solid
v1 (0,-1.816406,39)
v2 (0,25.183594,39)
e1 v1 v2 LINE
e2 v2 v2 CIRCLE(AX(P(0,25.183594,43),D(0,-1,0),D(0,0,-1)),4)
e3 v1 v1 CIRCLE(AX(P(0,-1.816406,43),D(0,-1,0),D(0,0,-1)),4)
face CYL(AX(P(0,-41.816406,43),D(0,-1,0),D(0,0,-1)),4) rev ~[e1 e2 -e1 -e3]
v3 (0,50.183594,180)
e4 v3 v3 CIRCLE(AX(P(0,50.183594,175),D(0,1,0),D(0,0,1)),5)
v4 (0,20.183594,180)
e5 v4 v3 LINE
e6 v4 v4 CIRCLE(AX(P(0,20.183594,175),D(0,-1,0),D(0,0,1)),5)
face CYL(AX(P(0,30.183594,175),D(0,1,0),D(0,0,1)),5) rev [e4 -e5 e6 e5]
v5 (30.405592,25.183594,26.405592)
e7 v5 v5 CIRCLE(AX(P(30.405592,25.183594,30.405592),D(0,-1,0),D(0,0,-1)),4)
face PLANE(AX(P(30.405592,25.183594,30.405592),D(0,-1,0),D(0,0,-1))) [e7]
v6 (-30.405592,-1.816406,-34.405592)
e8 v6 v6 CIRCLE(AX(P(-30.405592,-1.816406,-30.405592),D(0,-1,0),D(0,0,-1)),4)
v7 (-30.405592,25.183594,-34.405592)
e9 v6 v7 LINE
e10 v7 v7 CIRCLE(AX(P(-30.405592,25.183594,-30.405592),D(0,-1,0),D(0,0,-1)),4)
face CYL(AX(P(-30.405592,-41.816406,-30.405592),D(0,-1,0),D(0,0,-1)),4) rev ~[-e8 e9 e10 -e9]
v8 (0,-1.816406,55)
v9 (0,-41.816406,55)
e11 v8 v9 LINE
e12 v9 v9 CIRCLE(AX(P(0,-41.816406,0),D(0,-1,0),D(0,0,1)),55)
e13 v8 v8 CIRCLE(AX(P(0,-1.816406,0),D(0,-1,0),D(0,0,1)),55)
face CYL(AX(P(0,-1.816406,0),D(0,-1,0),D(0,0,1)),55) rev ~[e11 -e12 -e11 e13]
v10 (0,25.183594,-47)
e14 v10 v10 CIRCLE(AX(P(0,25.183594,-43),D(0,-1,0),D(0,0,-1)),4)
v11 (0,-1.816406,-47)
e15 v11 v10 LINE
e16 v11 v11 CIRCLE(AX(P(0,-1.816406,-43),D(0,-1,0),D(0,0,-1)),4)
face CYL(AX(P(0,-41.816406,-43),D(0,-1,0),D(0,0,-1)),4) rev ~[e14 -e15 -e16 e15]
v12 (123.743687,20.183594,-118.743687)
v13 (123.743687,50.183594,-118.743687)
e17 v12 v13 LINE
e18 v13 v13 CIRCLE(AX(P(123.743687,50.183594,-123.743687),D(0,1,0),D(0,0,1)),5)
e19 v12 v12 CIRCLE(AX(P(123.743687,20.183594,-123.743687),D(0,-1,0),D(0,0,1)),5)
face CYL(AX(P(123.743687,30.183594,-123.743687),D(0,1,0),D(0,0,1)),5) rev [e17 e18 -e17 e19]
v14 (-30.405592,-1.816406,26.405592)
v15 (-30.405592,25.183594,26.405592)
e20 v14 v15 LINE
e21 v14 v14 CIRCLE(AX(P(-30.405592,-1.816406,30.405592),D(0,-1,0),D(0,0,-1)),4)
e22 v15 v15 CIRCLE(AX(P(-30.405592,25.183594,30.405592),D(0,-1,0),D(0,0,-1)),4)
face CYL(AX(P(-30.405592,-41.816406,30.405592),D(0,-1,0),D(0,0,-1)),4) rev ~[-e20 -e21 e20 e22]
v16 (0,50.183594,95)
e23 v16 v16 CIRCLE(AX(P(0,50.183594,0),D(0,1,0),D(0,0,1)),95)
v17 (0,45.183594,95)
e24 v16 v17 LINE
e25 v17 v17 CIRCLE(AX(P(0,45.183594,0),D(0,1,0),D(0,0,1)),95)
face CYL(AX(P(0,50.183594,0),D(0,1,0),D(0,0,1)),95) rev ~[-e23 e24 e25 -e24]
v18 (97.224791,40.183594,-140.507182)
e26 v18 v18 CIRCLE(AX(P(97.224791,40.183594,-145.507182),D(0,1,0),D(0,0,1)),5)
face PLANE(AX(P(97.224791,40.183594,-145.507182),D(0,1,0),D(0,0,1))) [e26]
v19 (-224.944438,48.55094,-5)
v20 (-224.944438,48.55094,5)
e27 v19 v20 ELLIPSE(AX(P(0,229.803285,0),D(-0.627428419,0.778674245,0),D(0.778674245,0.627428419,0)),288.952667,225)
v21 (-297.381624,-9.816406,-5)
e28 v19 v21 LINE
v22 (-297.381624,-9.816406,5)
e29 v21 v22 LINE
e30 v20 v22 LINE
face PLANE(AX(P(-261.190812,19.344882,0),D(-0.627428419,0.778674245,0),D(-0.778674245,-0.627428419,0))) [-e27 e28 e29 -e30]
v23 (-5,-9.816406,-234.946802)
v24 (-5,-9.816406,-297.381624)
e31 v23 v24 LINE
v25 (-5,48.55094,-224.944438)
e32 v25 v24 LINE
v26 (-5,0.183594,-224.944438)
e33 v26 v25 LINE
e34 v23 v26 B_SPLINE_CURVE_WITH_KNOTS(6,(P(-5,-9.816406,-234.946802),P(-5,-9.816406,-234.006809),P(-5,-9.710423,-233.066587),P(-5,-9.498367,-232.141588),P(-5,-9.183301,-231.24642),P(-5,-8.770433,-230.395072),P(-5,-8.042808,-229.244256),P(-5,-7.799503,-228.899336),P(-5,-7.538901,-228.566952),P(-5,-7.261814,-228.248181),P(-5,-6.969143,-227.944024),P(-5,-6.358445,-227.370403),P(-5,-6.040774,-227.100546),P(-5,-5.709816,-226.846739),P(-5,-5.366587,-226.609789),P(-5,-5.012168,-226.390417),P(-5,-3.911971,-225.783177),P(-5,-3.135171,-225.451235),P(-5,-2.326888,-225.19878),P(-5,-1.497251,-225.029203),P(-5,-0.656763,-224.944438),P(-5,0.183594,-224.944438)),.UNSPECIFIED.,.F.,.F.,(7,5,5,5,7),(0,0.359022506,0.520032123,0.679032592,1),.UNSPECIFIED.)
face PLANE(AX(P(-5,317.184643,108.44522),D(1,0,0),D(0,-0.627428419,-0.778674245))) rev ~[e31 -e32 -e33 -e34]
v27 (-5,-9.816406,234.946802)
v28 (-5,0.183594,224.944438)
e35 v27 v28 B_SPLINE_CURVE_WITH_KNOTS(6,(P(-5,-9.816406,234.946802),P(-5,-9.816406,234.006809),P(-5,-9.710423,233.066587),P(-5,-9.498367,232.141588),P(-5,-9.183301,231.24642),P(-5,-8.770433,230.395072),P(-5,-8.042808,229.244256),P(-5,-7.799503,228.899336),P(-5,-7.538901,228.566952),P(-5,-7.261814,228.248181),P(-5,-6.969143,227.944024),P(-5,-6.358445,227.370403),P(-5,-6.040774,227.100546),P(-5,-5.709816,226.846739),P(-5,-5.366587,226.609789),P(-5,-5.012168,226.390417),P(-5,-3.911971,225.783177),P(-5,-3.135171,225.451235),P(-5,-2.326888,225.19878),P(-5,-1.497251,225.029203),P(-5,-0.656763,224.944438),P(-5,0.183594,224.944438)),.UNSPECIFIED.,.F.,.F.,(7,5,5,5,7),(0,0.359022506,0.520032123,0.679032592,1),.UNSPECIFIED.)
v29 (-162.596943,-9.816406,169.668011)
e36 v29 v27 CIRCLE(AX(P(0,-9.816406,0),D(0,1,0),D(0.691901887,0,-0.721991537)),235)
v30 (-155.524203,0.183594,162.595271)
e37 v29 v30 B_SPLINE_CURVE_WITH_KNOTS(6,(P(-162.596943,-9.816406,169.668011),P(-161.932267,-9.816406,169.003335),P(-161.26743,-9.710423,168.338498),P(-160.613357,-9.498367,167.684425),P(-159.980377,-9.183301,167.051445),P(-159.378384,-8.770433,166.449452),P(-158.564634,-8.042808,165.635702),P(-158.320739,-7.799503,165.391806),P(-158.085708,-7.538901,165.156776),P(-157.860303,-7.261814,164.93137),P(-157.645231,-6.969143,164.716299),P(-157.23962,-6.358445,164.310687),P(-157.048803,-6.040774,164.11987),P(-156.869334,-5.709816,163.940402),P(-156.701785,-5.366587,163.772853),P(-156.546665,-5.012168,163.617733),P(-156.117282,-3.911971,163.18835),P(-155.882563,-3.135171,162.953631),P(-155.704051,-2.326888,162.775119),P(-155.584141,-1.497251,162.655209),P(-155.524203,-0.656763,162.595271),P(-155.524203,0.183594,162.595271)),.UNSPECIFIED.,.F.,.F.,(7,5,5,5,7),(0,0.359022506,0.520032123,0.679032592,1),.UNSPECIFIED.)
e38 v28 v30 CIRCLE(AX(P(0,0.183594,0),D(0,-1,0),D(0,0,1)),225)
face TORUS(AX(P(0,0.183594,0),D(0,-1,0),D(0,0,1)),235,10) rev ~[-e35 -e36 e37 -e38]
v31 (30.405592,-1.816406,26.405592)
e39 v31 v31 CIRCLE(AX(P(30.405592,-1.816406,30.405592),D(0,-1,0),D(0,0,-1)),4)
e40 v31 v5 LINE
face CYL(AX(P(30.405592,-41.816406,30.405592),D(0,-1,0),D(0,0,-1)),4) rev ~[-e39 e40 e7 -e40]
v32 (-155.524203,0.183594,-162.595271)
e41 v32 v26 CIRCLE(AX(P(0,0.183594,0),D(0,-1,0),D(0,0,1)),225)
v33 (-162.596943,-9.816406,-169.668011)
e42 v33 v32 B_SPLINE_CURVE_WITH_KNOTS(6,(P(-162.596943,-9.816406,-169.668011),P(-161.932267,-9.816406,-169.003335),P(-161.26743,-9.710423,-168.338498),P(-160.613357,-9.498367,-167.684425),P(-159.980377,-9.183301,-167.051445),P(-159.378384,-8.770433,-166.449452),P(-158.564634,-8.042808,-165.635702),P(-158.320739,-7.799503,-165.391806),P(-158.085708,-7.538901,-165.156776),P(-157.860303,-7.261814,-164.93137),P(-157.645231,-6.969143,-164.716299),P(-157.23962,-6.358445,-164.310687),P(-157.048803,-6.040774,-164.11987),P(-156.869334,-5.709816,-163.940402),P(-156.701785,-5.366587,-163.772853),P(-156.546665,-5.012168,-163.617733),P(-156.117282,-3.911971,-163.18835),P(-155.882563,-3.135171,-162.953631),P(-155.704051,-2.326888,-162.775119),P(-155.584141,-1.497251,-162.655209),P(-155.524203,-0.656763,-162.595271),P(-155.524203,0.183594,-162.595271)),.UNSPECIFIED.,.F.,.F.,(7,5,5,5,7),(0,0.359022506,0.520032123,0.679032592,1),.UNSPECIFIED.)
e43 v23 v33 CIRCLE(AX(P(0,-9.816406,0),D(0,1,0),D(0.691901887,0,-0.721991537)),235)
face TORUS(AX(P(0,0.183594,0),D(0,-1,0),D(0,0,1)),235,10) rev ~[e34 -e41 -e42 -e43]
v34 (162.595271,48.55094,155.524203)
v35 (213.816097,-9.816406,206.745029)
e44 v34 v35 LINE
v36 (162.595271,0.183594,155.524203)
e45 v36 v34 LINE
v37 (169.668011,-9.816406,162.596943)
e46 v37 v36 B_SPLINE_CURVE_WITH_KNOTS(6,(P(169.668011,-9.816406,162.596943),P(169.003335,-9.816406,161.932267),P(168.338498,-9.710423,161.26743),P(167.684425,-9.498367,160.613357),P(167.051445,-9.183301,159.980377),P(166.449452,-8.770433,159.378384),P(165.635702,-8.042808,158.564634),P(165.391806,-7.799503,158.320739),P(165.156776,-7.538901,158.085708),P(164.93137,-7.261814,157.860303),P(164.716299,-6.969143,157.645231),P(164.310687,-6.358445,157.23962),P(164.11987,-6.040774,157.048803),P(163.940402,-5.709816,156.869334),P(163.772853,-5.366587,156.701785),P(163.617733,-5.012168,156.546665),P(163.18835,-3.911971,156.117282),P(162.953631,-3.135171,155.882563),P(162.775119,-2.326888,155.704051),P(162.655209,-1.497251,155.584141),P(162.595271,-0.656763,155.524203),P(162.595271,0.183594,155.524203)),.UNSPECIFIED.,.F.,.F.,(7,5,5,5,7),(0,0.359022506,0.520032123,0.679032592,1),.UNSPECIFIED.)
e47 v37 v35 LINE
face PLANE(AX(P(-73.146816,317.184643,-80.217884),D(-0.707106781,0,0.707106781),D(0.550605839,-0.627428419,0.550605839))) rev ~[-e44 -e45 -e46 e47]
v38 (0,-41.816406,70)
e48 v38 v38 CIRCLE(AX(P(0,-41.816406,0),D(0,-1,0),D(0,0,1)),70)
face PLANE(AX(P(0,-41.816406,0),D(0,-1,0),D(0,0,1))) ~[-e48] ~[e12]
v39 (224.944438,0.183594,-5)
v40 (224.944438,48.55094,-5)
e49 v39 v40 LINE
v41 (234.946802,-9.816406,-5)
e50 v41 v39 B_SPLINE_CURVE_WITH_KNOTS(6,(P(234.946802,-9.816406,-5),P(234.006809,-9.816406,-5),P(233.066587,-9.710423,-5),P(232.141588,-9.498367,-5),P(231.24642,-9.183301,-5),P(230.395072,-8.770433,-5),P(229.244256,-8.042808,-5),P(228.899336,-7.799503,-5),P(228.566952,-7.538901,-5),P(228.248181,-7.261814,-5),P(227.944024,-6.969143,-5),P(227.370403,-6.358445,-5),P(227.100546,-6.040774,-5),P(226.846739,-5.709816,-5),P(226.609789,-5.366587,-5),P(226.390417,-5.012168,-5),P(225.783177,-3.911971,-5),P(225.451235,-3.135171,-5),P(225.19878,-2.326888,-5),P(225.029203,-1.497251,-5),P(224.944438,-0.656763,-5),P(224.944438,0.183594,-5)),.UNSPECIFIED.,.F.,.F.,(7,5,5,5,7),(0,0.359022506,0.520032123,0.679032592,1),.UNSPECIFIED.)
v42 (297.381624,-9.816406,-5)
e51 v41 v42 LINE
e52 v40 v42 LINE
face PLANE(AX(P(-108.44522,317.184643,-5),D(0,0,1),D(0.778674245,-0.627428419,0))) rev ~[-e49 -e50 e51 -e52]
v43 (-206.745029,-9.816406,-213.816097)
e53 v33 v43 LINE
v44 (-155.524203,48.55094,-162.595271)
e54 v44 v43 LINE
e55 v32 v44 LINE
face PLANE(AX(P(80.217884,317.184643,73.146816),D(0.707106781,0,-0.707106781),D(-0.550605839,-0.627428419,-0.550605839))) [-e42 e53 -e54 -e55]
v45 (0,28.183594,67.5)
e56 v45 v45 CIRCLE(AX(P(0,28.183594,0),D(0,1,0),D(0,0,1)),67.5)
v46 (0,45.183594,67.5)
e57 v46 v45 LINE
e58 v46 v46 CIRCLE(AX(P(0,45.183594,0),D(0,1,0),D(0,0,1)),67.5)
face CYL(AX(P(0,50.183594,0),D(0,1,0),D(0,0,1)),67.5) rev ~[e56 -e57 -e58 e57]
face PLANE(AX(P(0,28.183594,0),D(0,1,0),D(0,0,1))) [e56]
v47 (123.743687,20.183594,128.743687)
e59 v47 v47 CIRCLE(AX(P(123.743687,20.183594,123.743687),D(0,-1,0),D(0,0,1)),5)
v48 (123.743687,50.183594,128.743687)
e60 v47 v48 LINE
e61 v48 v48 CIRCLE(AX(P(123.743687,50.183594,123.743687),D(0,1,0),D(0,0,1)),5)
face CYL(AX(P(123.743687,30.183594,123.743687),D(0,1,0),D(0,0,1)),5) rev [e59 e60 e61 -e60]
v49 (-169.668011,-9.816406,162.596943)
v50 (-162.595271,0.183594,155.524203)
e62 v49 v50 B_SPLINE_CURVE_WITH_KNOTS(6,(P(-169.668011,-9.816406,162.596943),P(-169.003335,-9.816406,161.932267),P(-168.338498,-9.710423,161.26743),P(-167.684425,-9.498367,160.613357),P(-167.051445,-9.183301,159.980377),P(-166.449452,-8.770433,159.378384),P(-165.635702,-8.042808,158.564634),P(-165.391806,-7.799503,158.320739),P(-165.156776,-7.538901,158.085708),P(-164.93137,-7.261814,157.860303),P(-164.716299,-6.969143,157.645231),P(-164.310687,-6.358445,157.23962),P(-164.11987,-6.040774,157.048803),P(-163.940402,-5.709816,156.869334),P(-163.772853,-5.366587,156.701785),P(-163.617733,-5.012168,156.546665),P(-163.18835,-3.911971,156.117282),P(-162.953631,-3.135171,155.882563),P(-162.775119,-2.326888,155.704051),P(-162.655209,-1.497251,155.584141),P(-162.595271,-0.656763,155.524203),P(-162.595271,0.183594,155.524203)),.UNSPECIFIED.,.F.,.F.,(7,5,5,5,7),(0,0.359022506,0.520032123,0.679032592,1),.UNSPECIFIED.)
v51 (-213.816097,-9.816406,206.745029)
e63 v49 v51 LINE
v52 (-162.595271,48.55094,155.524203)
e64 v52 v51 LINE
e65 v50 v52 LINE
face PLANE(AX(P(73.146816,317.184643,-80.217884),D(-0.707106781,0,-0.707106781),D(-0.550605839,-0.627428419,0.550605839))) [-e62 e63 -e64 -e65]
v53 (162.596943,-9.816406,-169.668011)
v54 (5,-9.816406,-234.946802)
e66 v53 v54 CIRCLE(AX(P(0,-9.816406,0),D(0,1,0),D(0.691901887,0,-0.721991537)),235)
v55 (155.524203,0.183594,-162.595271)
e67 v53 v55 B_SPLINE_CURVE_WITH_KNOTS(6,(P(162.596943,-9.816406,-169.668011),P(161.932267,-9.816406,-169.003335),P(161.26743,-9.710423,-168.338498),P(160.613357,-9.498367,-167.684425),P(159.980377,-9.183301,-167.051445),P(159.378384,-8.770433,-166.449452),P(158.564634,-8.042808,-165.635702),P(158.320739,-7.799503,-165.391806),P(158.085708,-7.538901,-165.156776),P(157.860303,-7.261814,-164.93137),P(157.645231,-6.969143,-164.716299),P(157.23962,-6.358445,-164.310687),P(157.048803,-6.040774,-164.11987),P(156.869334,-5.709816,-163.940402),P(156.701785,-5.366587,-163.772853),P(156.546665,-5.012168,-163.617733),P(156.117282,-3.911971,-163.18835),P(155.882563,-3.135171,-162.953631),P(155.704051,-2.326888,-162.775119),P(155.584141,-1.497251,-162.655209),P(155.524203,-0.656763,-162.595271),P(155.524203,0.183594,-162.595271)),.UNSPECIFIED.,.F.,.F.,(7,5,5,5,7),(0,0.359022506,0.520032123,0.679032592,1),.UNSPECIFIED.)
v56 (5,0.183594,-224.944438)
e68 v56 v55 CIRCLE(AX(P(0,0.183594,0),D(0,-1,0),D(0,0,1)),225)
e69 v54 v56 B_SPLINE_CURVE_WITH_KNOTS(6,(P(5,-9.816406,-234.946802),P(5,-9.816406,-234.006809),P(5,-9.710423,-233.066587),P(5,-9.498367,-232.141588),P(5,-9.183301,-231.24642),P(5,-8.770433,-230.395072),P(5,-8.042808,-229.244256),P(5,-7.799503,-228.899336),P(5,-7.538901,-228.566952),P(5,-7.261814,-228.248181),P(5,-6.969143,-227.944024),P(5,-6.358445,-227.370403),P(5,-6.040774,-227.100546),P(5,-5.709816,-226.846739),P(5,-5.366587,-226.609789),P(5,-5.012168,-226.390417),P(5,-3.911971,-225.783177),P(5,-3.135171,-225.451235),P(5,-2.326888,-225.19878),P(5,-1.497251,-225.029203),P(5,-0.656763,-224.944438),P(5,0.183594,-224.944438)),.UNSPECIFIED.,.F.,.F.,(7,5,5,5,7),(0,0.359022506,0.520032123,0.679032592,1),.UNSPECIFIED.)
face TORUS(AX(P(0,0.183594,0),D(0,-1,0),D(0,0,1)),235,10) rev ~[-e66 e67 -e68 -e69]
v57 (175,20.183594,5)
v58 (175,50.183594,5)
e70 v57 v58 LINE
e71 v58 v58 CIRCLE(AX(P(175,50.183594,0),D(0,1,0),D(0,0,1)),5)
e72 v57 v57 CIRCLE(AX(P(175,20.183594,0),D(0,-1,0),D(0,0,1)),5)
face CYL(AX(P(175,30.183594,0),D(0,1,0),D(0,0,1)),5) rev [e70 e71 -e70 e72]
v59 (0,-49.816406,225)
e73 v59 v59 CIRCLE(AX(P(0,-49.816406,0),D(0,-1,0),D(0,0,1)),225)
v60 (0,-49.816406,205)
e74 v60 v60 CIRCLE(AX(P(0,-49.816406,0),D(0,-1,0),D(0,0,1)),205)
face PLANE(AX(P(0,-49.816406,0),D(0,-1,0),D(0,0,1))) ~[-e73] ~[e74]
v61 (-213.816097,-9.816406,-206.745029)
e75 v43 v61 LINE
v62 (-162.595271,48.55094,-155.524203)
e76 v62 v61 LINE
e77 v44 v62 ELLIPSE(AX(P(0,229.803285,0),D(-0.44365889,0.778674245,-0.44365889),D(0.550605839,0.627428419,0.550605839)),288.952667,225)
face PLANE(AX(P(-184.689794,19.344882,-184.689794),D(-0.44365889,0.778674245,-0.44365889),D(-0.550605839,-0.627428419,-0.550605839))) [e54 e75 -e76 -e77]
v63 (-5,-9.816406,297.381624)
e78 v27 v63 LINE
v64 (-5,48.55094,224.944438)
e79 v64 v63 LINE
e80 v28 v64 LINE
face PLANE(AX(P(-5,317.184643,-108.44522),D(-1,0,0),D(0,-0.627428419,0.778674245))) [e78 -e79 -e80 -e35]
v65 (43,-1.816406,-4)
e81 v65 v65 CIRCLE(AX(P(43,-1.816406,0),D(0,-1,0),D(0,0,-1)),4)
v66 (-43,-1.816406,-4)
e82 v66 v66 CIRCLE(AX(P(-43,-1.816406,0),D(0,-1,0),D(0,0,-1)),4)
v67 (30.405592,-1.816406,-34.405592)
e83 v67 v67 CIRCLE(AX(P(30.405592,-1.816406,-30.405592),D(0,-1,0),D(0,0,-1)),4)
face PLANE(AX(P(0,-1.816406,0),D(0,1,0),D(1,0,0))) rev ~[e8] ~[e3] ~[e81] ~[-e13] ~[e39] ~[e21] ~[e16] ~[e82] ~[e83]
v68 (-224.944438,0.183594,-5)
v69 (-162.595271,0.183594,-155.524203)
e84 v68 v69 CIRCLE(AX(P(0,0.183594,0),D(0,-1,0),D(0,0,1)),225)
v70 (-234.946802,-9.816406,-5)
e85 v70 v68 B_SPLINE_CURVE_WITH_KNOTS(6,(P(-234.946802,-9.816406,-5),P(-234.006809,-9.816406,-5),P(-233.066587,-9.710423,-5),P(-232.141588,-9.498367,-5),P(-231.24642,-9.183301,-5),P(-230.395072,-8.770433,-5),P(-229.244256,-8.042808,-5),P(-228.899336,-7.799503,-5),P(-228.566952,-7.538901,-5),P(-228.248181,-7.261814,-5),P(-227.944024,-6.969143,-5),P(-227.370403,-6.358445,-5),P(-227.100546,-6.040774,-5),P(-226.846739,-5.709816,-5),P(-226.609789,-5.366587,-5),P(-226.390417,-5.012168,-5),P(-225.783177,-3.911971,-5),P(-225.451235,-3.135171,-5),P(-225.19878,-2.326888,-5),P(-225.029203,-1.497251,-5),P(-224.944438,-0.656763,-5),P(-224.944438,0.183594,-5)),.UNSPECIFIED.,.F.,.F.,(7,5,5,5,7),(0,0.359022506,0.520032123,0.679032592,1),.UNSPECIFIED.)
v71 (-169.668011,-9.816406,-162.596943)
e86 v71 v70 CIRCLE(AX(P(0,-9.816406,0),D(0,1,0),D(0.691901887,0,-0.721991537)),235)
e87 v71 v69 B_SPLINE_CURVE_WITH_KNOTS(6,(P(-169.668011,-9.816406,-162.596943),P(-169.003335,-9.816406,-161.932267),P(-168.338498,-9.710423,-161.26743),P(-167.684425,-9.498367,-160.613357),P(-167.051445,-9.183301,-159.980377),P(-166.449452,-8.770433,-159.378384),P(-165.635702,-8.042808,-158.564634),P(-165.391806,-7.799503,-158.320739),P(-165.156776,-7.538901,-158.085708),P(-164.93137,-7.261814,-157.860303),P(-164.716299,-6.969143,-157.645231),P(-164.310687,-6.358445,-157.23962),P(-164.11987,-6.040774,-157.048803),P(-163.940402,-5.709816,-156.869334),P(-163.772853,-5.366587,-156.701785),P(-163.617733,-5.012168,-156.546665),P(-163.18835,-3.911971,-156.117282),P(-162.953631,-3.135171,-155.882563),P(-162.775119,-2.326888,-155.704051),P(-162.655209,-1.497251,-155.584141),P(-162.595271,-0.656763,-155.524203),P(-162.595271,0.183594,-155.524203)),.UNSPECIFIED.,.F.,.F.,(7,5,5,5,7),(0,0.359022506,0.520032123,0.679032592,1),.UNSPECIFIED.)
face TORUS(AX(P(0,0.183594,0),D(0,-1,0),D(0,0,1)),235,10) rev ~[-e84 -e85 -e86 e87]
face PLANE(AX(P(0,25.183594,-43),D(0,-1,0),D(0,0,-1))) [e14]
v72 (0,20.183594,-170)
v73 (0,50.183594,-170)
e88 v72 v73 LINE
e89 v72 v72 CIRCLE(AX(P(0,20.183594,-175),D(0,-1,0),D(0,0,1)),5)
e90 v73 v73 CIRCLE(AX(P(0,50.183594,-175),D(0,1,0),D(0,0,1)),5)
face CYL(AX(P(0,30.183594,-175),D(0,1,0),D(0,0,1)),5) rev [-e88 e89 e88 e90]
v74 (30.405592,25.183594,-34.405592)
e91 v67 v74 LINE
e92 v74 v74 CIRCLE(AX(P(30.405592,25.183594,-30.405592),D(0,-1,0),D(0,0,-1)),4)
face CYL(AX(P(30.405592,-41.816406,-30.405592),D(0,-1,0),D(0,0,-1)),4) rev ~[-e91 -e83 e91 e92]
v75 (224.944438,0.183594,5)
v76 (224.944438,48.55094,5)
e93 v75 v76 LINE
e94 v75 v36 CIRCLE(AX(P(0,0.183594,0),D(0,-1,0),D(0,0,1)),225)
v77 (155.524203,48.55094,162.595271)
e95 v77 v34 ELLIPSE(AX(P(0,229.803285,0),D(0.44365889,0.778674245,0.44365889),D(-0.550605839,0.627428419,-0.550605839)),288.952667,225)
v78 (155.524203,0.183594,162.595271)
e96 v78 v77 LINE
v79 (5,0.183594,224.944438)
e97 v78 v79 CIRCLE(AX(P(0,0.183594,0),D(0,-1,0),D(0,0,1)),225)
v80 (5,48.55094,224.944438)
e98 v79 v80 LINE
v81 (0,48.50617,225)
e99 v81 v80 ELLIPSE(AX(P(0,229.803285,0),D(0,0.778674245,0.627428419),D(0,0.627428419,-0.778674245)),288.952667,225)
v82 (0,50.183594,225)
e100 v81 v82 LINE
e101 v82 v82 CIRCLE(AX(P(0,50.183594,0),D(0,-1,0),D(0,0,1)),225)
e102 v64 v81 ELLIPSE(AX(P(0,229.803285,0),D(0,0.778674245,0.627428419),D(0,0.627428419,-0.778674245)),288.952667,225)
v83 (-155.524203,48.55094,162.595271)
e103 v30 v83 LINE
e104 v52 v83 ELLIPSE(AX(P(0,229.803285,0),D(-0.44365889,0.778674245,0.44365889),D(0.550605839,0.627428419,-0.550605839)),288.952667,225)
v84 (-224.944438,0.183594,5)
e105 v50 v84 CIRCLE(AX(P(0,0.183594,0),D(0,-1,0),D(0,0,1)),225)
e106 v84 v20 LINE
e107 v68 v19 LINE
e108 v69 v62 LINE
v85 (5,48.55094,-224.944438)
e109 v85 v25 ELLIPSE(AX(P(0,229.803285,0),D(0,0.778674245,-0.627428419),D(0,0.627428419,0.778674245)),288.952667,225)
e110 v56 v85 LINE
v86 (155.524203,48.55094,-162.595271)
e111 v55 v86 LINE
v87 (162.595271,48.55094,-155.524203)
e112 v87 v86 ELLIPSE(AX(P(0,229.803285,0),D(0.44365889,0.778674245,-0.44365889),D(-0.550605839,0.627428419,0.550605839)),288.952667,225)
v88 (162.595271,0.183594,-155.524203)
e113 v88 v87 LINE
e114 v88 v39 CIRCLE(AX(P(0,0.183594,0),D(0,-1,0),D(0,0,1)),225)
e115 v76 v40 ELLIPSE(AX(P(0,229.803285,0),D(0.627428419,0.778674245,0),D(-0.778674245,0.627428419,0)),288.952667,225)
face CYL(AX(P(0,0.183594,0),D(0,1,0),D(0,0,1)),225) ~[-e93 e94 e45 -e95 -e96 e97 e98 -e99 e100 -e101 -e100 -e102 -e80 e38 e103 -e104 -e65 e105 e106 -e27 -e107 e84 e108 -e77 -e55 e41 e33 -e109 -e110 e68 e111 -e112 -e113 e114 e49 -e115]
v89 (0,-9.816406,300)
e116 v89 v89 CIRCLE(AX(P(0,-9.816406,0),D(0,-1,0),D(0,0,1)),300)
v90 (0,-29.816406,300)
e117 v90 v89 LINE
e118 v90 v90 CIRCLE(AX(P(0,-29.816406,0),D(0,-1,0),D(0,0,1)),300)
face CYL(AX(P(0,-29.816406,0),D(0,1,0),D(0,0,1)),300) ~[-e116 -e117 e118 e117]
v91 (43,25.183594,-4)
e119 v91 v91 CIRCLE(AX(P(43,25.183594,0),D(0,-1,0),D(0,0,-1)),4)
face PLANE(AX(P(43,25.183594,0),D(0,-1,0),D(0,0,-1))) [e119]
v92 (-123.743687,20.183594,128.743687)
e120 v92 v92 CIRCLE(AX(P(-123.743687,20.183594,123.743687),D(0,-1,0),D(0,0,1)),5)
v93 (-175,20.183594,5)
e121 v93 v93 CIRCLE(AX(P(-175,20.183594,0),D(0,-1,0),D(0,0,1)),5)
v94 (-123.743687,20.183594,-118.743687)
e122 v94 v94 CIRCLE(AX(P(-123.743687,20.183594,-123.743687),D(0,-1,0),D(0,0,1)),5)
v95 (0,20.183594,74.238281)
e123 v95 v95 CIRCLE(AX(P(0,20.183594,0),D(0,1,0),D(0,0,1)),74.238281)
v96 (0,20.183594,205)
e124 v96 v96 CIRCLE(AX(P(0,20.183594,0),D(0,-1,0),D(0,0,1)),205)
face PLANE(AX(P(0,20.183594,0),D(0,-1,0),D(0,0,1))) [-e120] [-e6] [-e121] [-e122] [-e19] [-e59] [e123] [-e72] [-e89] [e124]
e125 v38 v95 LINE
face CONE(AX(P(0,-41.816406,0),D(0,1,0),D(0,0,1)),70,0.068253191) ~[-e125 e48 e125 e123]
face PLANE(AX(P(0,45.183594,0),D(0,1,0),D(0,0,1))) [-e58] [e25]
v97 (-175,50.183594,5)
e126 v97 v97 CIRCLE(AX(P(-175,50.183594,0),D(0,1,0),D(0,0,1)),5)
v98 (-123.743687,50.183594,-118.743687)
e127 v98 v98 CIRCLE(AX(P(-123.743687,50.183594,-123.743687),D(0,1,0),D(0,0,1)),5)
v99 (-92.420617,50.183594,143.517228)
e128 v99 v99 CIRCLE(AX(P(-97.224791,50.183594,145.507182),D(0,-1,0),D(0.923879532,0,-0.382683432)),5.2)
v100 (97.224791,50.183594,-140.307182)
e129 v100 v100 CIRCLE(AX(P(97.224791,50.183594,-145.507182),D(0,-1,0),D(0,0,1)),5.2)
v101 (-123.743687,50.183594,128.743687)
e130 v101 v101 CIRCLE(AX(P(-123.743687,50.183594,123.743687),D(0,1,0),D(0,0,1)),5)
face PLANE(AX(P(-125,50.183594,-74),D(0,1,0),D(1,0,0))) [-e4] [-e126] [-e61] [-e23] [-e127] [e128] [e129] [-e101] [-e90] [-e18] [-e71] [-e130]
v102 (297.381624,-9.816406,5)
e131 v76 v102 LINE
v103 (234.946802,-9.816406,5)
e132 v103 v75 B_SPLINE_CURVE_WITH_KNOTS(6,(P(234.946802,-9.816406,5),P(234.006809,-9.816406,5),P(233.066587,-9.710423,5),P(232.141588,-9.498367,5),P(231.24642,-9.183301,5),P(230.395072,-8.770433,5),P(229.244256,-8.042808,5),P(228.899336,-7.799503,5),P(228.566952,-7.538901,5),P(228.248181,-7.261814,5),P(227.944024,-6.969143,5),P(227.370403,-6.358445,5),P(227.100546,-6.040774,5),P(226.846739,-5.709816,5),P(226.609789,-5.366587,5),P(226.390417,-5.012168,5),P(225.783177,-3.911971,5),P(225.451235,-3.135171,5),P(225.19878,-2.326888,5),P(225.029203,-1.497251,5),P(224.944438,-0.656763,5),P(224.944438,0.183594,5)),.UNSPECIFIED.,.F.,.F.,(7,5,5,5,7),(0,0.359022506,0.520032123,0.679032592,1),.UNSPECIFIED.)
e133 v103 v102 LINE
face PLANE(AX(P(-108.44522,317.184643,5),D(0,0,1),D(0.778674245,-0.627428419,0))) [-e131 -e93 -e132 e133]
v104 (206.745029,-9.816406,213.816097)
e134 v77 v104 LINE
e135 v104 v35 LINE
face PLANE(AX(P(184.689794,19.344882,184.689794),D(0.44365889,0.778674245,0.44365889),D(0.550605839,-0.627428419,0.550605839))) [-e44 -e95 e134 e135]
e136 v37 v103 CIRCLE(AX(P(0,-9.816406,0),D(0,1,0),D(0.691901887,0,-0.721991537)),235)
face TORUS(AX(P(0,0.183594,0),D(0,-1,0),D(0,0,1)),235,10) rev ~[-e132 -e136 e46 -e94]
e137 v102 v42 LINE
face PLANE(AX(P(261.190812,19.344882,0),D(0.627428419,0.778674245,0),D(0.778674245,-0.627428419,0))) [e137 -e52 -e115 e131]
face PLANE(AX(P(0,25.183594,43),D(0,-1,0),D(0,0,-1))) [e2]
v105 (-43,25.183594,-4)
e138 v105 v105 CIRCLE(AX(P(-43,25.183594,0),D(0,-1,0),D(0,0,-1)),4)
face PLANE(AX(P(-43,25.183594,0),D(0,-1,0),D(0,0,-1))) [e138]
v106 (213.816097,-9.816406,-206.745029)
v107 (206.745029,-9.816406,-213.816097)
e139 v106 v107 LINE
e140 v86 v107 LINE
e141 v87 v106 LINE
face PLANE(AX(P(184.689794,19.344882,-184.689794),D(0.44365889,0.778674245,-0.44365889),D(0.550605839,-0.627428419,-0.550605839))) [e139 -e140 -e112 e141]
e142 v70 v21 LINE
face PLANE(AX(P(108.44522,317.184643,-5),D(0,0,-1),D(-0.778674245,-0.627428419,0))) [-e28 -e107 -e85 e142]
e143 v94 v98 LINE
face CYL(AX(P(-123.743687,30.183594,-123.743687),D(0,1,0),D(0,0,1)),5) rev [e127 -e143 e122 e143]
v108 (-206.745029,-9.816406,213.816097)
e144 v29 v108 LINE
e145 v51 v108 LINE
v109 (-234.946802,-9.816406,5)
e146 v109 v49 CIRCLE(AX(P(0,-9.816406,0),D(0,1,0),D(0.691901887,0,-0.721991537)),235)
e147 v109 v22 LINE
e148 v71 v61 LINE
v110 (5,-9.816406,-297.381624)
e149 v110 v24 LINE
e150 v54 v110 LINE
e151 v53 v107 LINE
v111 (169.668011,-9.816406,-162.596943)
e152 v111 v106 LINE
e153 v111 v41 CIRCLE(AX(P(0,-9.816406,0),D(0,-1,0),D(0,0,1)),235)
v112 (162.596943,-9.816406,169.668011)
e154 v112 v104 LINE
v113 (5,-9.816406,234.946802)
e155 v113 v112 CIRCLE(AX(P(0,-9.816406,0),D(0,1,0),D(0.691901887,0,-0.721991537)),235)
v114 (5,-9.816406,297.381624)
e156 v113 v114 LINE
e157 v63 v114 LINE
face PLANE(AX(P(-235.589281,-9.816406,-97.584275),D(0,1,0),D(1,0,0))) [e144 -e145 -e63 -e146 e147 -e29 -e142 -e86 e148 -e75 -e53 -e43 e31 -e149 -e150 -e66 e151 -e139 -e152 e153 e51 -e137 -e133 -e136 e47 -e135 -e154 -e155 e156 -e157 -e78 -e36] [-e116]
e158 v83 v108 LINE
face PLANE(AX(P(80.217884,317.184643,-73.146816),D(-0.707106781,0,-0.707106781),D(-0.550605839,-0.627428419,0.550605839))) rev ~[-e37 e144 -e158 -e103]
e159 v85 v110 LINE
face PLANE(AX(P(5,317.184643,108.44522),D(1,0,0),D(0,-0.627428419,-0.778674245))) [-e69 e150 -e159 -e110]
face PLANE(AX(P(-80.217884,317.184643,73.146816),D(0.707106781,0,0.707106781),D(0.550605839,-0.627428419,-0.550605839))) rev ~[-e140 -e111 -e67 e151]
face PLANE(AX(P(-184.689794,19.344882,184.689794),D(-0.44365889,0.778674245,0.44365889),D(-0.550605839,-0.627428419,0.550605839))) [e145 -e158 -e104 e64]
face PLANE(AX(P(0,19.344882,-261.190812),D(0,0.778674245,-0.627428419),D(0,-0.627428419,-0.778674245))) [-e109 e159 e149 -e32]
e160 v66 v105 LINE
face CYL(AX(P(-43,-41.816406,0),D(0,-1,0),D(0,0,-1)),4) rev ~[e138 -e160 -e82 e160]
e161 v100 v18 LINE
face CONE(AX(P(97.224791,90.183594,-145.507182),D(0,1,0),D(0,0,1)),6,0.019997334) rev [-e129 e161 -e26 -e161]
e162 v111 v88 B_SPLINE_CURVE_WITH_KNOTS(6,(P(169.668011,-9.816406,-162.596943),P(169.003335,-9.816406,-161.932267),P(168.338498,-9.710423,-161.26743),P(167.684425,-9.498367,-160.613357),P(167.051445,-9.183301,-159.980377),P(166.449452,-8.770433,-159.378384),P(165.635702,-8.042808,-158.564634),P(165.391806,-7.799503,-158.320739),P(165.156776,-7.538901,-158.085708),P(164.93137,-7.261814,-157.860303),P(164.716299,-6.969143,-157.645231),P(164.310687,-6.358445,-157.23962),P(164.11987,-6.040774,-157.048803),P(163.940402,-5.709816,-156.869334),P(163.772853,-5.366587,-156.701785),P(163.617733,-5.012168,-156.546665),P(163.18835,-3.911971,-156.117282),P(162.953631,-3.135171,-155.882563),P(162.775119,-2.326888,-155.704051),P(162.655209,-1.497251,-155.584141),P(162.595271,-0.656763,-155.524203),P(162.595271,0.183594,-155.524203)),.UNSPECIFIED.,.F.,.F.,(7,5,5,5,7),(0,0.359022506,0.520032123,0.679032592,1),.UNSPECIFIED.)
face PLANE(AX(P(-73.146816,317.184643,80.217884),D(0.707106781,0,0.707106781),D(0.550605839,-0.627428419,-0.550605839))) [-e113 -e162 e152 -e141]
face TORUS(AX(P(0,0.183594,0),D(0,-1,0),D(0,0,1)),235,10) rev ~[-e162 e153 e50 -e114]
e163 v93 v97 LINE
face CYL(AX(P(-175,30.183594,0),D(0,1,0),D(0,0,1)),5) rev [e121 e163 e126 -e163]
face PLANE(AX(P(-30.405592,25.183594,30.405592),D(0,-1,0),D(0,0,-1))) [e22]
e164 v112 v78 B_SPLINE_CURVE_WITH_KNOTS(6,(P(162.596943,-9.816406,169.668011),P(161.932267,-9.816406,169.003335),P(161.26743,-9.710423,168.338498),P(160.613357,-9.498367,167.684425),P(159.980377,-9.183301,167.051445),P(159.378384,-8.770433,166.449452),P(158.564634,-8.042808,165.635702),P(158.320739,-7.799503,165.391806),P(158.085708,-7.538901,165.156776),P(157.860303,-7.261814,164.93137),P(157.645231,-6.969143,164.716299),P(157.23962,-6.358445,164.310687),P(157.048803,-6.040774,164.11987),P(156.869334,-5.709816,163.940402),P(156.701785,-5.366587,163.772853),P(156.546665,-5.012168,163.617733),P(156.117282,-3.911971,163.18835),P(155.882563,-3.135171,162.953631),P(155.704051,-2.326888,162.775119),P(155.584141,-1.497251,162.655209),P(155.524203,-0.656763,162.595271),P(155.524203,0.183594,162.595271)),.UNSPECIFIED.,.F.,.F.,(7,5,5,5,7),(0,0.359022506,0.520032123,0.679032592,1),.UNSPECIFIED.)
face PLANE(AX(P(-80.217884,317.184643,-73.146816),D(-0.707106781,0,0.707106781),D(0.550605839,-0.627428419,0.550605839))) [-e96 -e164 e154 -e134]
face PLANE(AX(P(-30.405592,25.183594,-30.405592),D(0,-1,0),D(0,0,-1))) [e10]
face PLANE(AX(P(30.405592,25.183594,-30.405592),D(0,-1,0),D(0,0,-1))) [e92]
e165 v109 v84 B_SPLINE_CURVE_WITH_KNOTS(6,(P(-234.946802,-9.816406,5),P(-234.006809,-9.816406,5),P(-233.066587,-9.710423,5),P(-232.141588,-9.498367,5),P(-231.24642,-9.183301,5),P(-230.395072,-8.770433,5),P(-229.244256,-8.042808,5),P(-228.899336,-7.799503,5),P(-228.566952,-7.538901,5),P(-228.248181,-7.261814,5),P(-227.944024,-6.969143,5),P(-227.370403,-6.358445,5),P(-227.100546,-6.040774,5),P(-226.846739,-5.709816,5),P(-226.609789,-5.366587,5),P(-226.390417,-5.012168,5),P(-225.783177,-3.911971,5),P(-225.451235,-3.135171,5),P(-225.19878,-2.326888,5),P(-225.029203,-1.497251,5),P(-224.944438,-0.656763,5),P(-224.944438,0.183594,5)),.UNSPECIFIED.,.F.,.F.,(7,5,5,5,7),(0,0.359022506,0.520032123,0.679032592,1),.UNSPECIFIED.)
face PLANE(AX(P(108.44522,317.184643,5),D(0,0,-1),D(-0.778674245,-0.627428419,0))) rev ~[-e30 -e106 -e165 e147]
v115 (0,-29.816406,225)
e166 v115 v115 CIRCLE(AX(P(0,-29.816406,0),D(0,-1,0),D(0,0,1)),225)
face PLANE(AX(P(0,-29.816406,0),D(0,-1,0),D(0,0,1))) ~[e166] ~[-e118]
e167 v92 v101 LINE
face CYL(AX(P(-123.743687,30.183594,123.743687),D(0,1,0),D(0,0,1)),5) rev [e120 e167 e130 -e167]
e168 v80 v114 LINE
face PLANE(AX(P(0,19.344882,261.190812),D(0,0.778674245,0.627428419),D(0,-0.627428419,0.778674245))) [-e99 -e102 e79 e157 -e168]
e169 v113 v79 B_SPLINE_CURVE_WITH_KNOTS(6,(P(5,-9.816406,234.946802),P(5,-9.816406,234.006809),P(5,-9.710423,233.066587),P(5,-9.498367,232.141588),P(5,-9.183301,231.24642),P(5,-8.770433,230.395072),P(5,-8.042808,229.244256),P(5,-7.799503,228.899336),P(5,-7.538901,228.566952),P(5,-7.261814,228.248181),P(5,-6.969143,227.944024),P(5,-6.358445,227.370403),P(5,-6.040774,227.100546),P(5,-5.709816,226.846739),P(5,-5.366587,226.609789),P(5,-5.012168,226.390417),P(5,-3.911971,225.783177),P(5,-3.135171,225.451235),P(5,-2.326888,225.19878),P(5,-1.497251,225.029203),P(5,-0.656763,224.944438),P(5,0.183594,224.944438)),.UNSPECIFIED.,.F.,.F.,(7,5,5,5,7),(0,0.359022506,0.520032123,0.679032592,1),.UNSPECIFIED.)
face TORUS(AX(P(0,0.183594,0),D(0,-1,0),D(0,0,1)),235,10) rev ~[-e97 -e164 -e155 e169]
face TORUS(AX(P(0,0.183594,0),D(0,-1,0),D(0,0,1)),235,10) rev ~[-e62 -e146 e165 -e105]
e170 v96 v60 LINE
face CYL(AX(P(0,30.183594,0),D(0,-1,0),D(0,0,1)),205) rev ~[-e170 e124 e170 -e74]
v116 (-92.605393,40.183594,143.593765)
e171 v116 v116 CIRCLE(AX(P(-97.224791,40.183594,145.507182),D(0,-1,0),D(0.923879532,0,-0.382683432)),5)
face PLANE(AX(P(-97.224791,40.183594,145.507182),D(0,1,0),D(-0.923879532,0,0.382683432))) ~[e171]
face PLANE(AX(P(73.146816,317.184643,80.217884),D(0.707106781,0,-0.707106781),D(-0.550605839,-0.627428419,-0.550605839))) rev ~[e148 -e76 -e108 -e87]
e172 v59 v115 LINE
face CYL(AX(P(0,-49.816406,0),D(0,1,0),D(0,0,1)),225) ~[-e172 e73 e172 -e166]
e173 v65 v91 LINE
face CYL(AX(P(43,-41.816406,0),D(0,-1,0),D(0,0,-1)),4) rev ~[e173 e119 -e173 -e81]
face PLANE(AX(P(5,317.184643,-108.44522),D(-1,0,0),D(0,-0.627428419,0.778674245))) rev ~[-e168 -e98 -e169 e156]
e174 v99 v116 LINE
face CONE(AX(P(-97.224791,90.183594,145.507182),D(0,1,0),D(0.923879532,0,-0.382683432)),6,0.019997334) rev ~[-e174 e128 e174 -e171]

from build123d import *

# Parameters (mm, degrees)
RIB_2_REACH              = 429.222
SKETCH_2_WALL_W          = 949.398376266
SKETCH_2_WALL_H          = 10
PATTERN_CIRCULAR_1_COUNT = 8
SKETCH_4_R               = 13
CUT_EXTRUDE_1_DEPTH      = 2
CUT_EXTRUDE_2_REACH      = 430.77
SKETCH_5_R               = 6.5
CUT_EXTRUDE_3_REACH      = 437.89
SKETCH_6_R               = 5
SKETCH_6_R_2             = 15
SKETCH_7_R               = 4
CUT_EXTRUDE_5_DEPTH      = 67
SKETCH_8_R               = 13
EXTRUDE_1_DEPTH          = 20
SKETCH_9_R               = 15
EXTRUDE_2_DEPTH          = 20
EXTRUDE_START            = -52
SKETCH_10_R              = 7.5
EXTRUDE_3_DEPTH          = 52
SKETCH_12_R              = 205
SKETCH_12_R_2            = 65
SKETCH_12_R_3            = 5
EXTRUDE_4_DEPTH          = 10
SKETCH_16_R              = 67.5
CUT_EXTRUDE_6_DEPTH      = 22
SKETCH_17_R              = 95
CUT_EXTRUDE_7_DEPTH      = 5


with BuildPart() as part:
    # 草图1 → 旋转1 (revolve)
    with BuildSketch(Plane.XY, mode=Mode.PRIVATE) as revolve_1_sk:
        with BuildLine():
            Line((7.5, 50.18359375), (7.5, -1.81640625))
            Line((7.5, -1.81640625), (55, -1.81640625))
            Line((55, -1.81640625), (55, -41.81640625))
            Line((55, -41.81640625), (70, -41.81640625))
            Line((70, -41.81640625), (74.921875, 30.18359375))
            Line((74.921875, 30.18359375), (205, 30.18359375))
            Line((205, 30.18359375), (205, -49.81640625))
            Line((205, -49.81640625), (225, -49.81640625))
            Line((225, -49.81640625), (225, -29.81640625))
            Line((225, -29.81640625), (300, -29.81640625))
            Line((300, -29.81640625), (300, -9.81640625))
            Line((300, -9.81640625), (235, -9.81640625))
            ThreePointArc((235, -9.81640625), (227.928932188, -6.887474062), (225, 0.18359375))
            Line((225, 0.18359375), (225, 50.18359375))
            Line((225, 50.18359375), (7.5, 50.18359375))
        make_face()
    revolve(revolve_1_sk.sketch.rotate(Axis((0, 22.32421875, 0), (0, -1, 0)), 90), axis=Axis((0, 22.32421875, 0), (0, -1, 0)))

    # 草图2 wall → 筋2 (add, up to next)
    with BuildSketch(Plane(origin=(261.190811903, 19.344881739, 0), x_dir=(0.778674244513, -0.62742841897, 0), z_dir=(0.62742841897, 0.778674244513, 0)), mode=Mode.PRIVATE) as rib_2_sk1:
        Rectangle(SKETCH_2_WALL_W, SKETCH_2_WALL_H)
    rib_2_tool1 = extrude(rib_2_sk1.sketch, amount=-RIB_2_REACH, mode=Mode.PRIVATE) - part.part
    rib_2 = rib_2_tool1.solids().sort_by_distance((261.190811903, 19.344881739, 0))[0]
    add(rib_2)

    # 阵列(圆周)1: 筋2 ×8 about axis
    pattern_circular_1_axis = Axis((0, 0, 0), (0, 1, 0))
    for i in range(1, PATTERN_CIRCULAR_1_COUNT):
        add(rib_2.rotate(pattern_circular_1_axis, i * 360 / PATTERN_CIRCULAR_1_COUNT))

    # 草图4 → 切除-拉伸1 (cut)
    with BuildSketch(Plane(origin=(0, -9.81640625, 0), x_dir=(1, 0, 0), z_dir=(0, 1, 0))):
        with Locations(Location((235.58928079, -97.584275253, 0), (0, 0, 270))):
            Circle(SKETCH_4_R)
        with Locations(Location((97.584275253, -235.58928079, 0), (0, 0, 270))):
            Circle(SKETCH_4_R)
        with Locations(Location((-97.584275253, -235.58928079, 0), (0, 0, 270))):
            Circle(SKETCH_4_R)
        with Locations(Location((-235.58928079, -97.584275253, 0), (0, 0, 270))):
            Circle(SKETCH_4_R)
        with Locations(Location((-235.58928079, 97.584275253, 0), (0, 0, 270))):
            Circle(SKETCH_4_R)
        with Locations(Location((-97.584275253, 235.58928079, 0), (0, 0, 270))):
            Circle(SKETCH_4_R)
        with Locations(Location((97.584275253, 235.58928079, 0), (0, 0, 270))):
            Circle(SKETCH_4_R)
        with Locations(Location((235.58928079, 97.584275253, 0), (0, 0, 270))):
            Circle(SKETCH_4_R)
    extrude(amount=-CUT_EXTRUDE_1_DEPTH, mode=Mode.SUBTRACT)

    # 草图5 → 切除-拉伸2 (cut, up to next)
    with BuildSketch(Plane(origin=(0, -11.81640625, 0), x_dir=(1, 0, 0), z_dir=(0, 1, 0)), mode=Mode.PRIVATE) as cut_extrude_2_sk1:
        with Locations(Location((235.58928079, 97.584275253, 0), (0, 0, 270))):
            Circle(SKETCH_5_R)
    cut_extrude_2_tool1 = extrude(cut_extrude_2_sk1.sketch, amount=-CUT_EXTRUDE_2_REACH, mode=Mode.PRIVATE) & part.part
    # 草图5 → 切除-拉伸2 (cut, up to next)
    with BuildSketch(Plane(origin=(0, -11.81640625, 0), x_dir=(1, 0, 0), z_dir=(0, 1, 0)), mode=Mode.PRIVATE) as cut_extrude_2_sk2:
        with Locations(Location((235.58928079, -97.584275253, 0), (0, 0, 270))):
            Circle(SKETCH_5_R)
    cut_extrude_2_tool2 = extrude(cut_extrude_2_sk2.sketch, amount=-CUT_EXTRUDE_2_REACH, mode=Mode.PRIVATE) & part.part
    # 草图5 → 切除-拉伸2 (cut, up to next)
    with BuildSketch(Plane(origin=(0, -11.81640625, 0), x_dir=(1, 0, 0), z_dir=(0, 1, 0)), mode=Mode.PRIVATE) as cut_extrude_2_sk3:
        with Locations(Location((97.584275253, -235.58928079, 0), (0, 0, 270))):
            Circle(SKETCH_5_R)
    cut_extrude_2_tool3 = extrude(cut_extrude_2_sk3.sketch, amount=-CUT_EXTRUDE_2_REACH, mode=Mode.PRIVATE) & part.part
    # 草图5 → 切除-拉伸2 (cut, up to next)
    with BuildSketch(Plane(origin=(0, -11.81640625, 0), x_dir=(1, 0, 0), z_dir=(0, 1, 0)), mode=Mode.PRIVATE) as cut_extrude_2_sk4:
        with Locations(Location((-97.584275253, -235.58928079, 0), (0, 0, 270))):
            Circle(SKETCH_5_R)
    cut_extrude_2_tool4 = extrude(cut_extrude_2_sk4.sketch, amount=-CUT_EXTRUDE_2_REACH, mode=Mode.PRIVATE) & part.part
    # 草图5 → 切除-拉伸2 (cut, up to next)
    with BuildSketch(Plane(origin=(0, -11.81640625, 0), x_dir=(1, 0, 0), z_dir=(0, 1, 0)), mode=Mode.PRIVATE) as cut_extrude_2_sk5:
        with Locations(Location((-235.58928079, -97.584275253, 0), (0, 0, 270))):
            Circle(SKETCH_5_R)
    cut_extrude_2_tool5 = extrude(cut_extrude_2_sk5.sketch, amount=-CUT_EXTRUDE_2_REACH, mode=Mode.PRIVATE) & part.part
    # 草图5 → 切除-拉伸2 (cut, up to next)
    with BuildSketch(Plane(origin=(0, -11.81640625, 0), x_dir=(1, 0, 0), z_dir=(0, 1, 0)), mode=Mode.PRIVATE) as cut_extrude_2_sk6:
        with Locations(Location((-235.58928079, 97.584275253, 0), (0, 0, 270))):
            Circle(SKETCH_5_R)
    cut_extrude_2_tool6 = extrude(cut_extrude_2_sk6.sketch, amount=-CUT_EXTRUDE_2_REACH, mode=Mode.PRIVATE) & part.part
    # 草图5 → 切除-拉伸2 (cut, up to next)
    with BuildSketch(Plane(origin=(0, -11.81640625, 0), x_dir=(1, 0, 0), z_dir=(0, 1, 0)), mode=Mode.PRIVATE) as cut_extrude_2_sk7:
        with Locations(Location((-97.584275253, 235.58928079, 0), (0, 0, 270))):
            Circle(SKETCH_5_R)
    cut_extrude_2_tool7 = extrude(cut_extrude_2_sk7.sketch, amount=-CUT_EXTRUDE_2_REACH, mode=Mode.PRIVATE) & part.part
    # 草图5 → 切除-拉伸2 (cut, up to next)
    with BuildSketch(Plane(origin=(0, -11.81640625, 0), x_dir=(1, 0, 0), z_dir=(0, 1, 0)), mode=Mode.PRIVATE) as cut_extrude_2_sk8:
        with Locations(Location((97.584275253, 235.58928079, 0), (0, 0, 270))):
            Circle(SKETCH_5_R)
    cut_extrude_2_tool8 = extrude(cut_extrude_2_sk8.sketch, amount=-CUT_EXTRUDE_2_REACH, mode=Mode.PRIVATE) & part.part
    add(cut_extrude_2_tool1.solids().sort_by_distance((235.589281, -11.816406, -97.584275))[0], mode=Mode.SUBTRACT)
    add(cut_extrude_2_tool2.solids().sort_by_distance((235.589281, -11.816406, 97.584275))[0], mode=Mode.SUBTRACT)
    add(cut_extrude_2_tool3.solids().sort_by_distance((97.584275, -11.816406, 235.589281))[0], mode=Mode.SUBTRACT)
    add(cut_extrude_2_tool4.solids().sort_by_distance((-97.584275, -11.816406, 235.589281))[0], mode=Mode.SUBTRACT)
    add(cut_extrude_2_tool5.solids().sort_by_distance((-235.589281, -11.816406, 97.584275))[0], mode=Mode.SUBTRACT)
    add(cut_extrude_2_tool6.solids().sort_by_distance((-235.589281, -11.816406, -97.584275))[0], mode=Mode.SUBTRACT)
    add(cut_extrude_2_tool7.solids().sort_by_distance((-97.584275, -11.816406, -235.589281))[0], mode=Mode.SUBTRACT)
    add(cut_extrude_2_tool8.solids().sort_by_distance((97.584275, -11.816406, -235.589281))[0], mode=Mode.SUBTRACT)

    # 草图6 → 切除-拉伸3 (cut, up to next)
    with BuildSketch(Plane(origin=(0, 50.18359375, 0), x_dir=(1, 0, 0), z_dir=(0, 1, 0)), mode=Mode.PRIVATE) as cut_extrude_3_sk1:
        with Locations(Location((175, 0, 0), (0, 0, 270))):
            Circle(SKETCH_6_R)
    cut_extrude_3_tool1 = extrude(cut_extrude_3_sk1.sketch, amount=-CUT_EXTRUDE_3_REACH, mode=Mode.PRIVATE) & part.part
    # 草图6 → 切除-拉伸3 (cut, up to next)
    with BuildSketch(Plane(origin=(0, 50.18359375, 0), x_dir=(1, 0, 0), z_dir=(0, 1, 0)), mode=Mode.PRIVATE) as cut_extrude_3_sk2:
        with Locations(Location((123.743686708, -123.743686708, 0), (0, 0, 270))):
            Circle(SKETCH_6_R)
    cut_extrude_3_tool2 = extrude(cut_extrude_3_sk2.sketch, amount=-CUT_EXTRUDE_3_REACH, mode=Mode.PRIVATE) & part.part
    # 草图6 → 切除-拉伸3 (cut, up to next)
    with BuildSketch(Plane(origin=(0, 50.18359375, 0), x_dir=(1, 0, 0), z_dir=(0, 1, 0)), mode=Mode.PRIVATE) as cut_extrude_3_sk3:
        with Locations(Location((0, -175, 0), (0, 0, 270))):
            Circle(SKETCH_6_R)
    cut_extrude_3_tool3 = extrude(cut_extrude_3_sk3.sketch, amount=-CUT_EXTRUDE_3_REACH, mode=Mode.PRIVATE) & part.part
    # 草图6 → 切除-拉伸3 (cut, up to next)
    with BuildSketch(Plane(origin=(0, 50.18359375, 0), x_dir=(1, 0, 0), z_dir=(0, 1, 0)), mode=Mode.PRIVATE) as cut_extrude_3_sk4:
        with Locations(Location((-123.743686708, -123.743686708, 0), (0, 0, 270))):
            Circle(SKETCH_6_R)
    cut_extrude_3_tool4 = extrude(cut_extrude_3_sk4.sketch, amount=-CUT_EXTRUDE_3_REACH, mode=Mode.PRIVATE) & part.part
    # 草图6 → 切除-拉伸3 (cut, up to next)
    with BuildSketch(Plane(origin=(0, 50.18359375, 0), x_dir=(1, 0, 0), z_dir=(0, 1, 0)), mode=Mode.PRIVATE) as cut_extrude_3_sk5:
        with Locations(Location((-175, 0, 0), (0, 0, 270))):
            Circle(SKETCH_6_R)
    cut_extrude_3_tool5 = extrude(cut_extrude_3_sk5.sketch, amount=-CUT_EXTRUDE_3_REACH, mode=Mode.PRIVATE) & part.part
    # 草图6 → 切除-拉伸3 (cut, up to next)
    with BuildSketch(Plane(origin=(0, 50.18359375, 0), x_dir=(1, 0, 0), z_dir=(0, 1, 0)), mode=Mode.PRIVATE) as cut_extrude_3_sk6:
        with Locations(Location((-123.743686708, 123.743686708, 0), (0, 0, 270))):
            Circle(SKETCH_6_R)
    cut_extrude_3_tool6 = extrude(cut_extrude_3_sk6.sketch, amount=-CUT_EXTRUDE_3_REACH, mode=Mode.PRIVATE) & part.part
    # 草图6 → 切除-拉伸3 (cut, up to next)
    with BuildSketch(Plane(origin=(0, 50.18359375, 0), x_dir=(1, 0, 0), z_dir=(0, 1, 0)), mode=Mode.PRIVATE) as cut_extrude_3_sk7:
        with Locations(Location((0, 175, 0), (0, 0, 270))):
            Circle(SKETCH_6_R)
    cut_extrude_3_tool7 = extrude(cut_extrude_3_sk7.sketch, amount=-CUT_EXTRUDE_3_REACH, mode=Mode.PRIVATE) & part.part
    # 草图6 → 切除-拉伸3 (cut, up to next)
    with BuildSketch(Plane(origin=(0, 50.18359375, 0), x_dir=(1, 0, 0), z_dir=(0, 1, 0)), mode=Mode.PRIVATE) as cut_extrude_3_sk8:
        with Locations(Location((123.743686708, 123.743686708, 0), (0, 0, 270))):
            Circle(SKETCH_6_R)
    cut_extrude_3_tool8 = extrude(cut_extrude_3_sk8.sketch, amount=-CUT_EXTRUDE_3_REACH, mode=Mode.PRIVATE) & part.part
    # 草图6 → 切除-拉伸3 (cut, up to next)
    with BuildSketch(Plane(origin=(0, 50.18359375, 0), x_dir=(1, 0, 0), z_dir=(0, 1, 0)), mode=Mode.PRIVATE) as cut_extrude_3_sk9:
        with Locations(Location((-125, 74, 0), (0, 0, 270))):
            Circle(SKETCH_6_R_2)
    cut_extrude_3_tool9 = extrude(cut_extrude_3_sk9.sketch, amount=-CUT_EXTRUDE_3_REACH, mode=Mode.PRIVATE) & part.part
    add(cut_extrude_3_tool1.solids().sort_by_distance((175, 50.183594, 0))[0], mode=Mode.SUBTRACT)
    add(cut_extrude_3_tool2.solids().sort_by_distance((123.743687, 50.183594, 123.743687))[0], mode=Mode.SUBTRACT)
    add(cut_extrude_3_tool3.solids().sort_by_distance((0, 50.183594, 175))[0], mode=Mode.SUBTRACT)
    add(cut_extrude_3_tool4.solids().sort_by_distance((-123.743687, 50.183594, 123.743687))[0], mode=Mode.SUBTRACT)
    add(cut_extrude_3_tool5.solids().sort_by_distance((-175, 50.183594, 0))[0], mode=Mode.SUBTRACT)
    add(cut_extrude_3_tool6.solids().sort_by_distance((-123.743687, 50.183594, -123.743687))[0], mode=Mode.SUBTRACT)
    add(cut_extrude_3_tool7.solids().sort_by_distance((0, 50.183594, -175))[0], mode=Mode.SUBTRACT)
    add(cut_extrude_3_tool8.solids().sort_by_distance((123.743687, 50.183594, -123.743687))[0], mode=Mode.SUBTRACT)
    add(cut_extrude_3_tool9.solids().sort_by_distance((-125, 50.183594, -74))[0], mode=Mode.SUBTRACT)

    # 草图7 → 切除-拉伸5 (cut)
    with BuildSketch(Plane.XZ.offset(41.81640625)):
        with Locations(Location((0, 43, 0), (0, 0, 270))):
            Circle(SKETCH_7_R)
        with Locations(Location((30.405591591, 30.405591591, 0), (0, 0, 270))):
            Circle(SKETCH_7_R)
        with Locations(Location((43, 0, 0), (0, 0, 270))):
            Circle(SKETCH_7_R)
        with Locations(Location((30.405591591, -30.405591591, 0), (0, 0, 270))):
            Circle(SKETCH_7_R)
        with Locations(Location((0, -43, 0), (0, 0, 270))):
            Circle(SKETCH_7_R)
        with Locations(Location((-30.405591591, -30.405591591, 0), (0, 0, 270))):
            Circle(SKETCH_7_R)
        with Locations(Location((-43, 0, 0), (0, 0, 270))):
            Circle(SKETCH_7_R)
        with Locations(Location((-30.405591591, 30.405591591, 0), (0, 0, 270))):
            Circle(SKETCH_7_R)
    extrude(amount=-CUT_EXTRUDE_5_DEPTH, mode=Mode.SUBTRACT)

    # 草图8 → 凸台-拉伸1 (add)
    with BuildSketch(Plane(origin=(0, -9.81640625, 0), x_dir=(1, 0, 0), z_dir=(0, 1, 0))):
        with Locations((-235.58928079, 97.584275253)):
            Circle(SKETCH_8_R)
        with Locations((-235.58928079, -97.584275253)):
            Circle(SKETCH_8_R)
        with Locations((-97.584275253, -235.58928079)):
            Circle(SKETCH_8_R)
        with Locations((97.584275253, -235.58928079)):
            Circle(SKETCH_8_R)
        with Locations((235.58928079, -97.584275253)):
            Circle(SKETCH_8_R)
        with Locations((235.58928079, 97.584275253)):
            Circle(SKETCH_8_R)
        with Locations((97.584275253, 235.58928079)):
            Circle(SKETCH_8_R)
        with Locations((-97.584275253, 235.58928079)):
            Circle(SKETCH_8_R)
    extrude(amount=-EXTRUDE_1_DEPTH)

    # 草图9 → 凸台-拉伸2 (add)
    with BuildSketch(Plane(origin=(0, 50.18359375, 0), x_dir=(1, 0, 0), z_dir=(0, 1, 0))):
        with Locations((-125, 74)):
            Circle(SKETCH_9_R)
    extrude(amount=-EXTRUDE_2_DEPTH)

    # 草图10 → 凸台-拉伸3 (add)
    with BuildSketch(Plane(origin=(0, 50.18359375, 0), x_dir=(1, 0, 0), z_dir=(0, 1, 0)).offset(EXTRUDE_START)):
        Circle(SKETCH_10_R)
    extrude(amount=EXTRUDE_3_DEPTH)

    # 草图12 → 凸台-拉伸4 (add)
    with BuildSketch(Plane.XZ.offset(-30.18359375)):
        with Locations(Location((0, 0, 0), (0, 0, 90))):
            Circle(SKETCH_12_R)
        Circle(SKETCH_12_R_2, mode=Mode.SUBTRACT)
        with Locations(Location((123.743686708, -123.743686708, 0), (0, 0, 90))):
            Circle(SKETCH_12_R_3, mode=Mode.SUBTRACT)
        with Locations(Location((0, -175, 0), (0, 0, 90))):
            Circle(SKETCH_12_R_3, mode=Mode.SUBTRACT)
        with Locations(Location((-123.743686708, -123.743686708, 0), (0, 0, 90))):
            Circle(SKETCH_12_R_3, mode=Mode.SUBTRACT)
        with Locations(Location((-175, 0, 0), (0, 0, 90))):
            Circle(SKETCH_12_R_3, mode=Mode.SUBTRACT)
        with Locations(Location((175, 0, 0), (0, 0, 90))):
            Circle(SKETCH_12_R_3, mode=Mode.SUBTRACT)
        with Locations(Location((123.743686708, 123.743686708, 0), (0, 0, 90))):
            Circle(SKETCH_12_R_3, mode=Mode.SUBTRACT)
        with Locations(Location((-123.743686708, 123.743686708, 0), (0, 0, 90))):
            Circle(SKETCH_12_R_3, mode=Mode.SUBTRACT)
        with Locations(Location((0, 175, 0), (0, 0, 90))):
            Circle(SKETCH_12_R_3, mode=Mode.SUBTRACT)
    extrude(amount=EXTRUDE_4_DEPTH)

    # 草图16 → 切除-拉伸6 (cut)
    with BuildSketch(Plane(origin=(0, 50.18359375, 0), x_dir=(1, 0, 0), z_dir=(0, 1, 0))):
        with Locations(Location((0, 0, 0), (0, 0, 270))):
            Circle(SKETCH_16_R)
    extrude(amount=-CUT_EXTRUDE_6_DEPTH, mode=Mode.SUBTRACT)

    # 草图17 → 切除-拉伸7 (cut)
    with BuildSketch(Plane(origin=(0, 50.18359375, 0), x_dir=(1, 0, 0), z_dir=(0, 1, 0))):
        with Locations(Location((0, 0, 0), (0, 0, 270))):
            Circle(SKETCH_17_R)
    extrude(amount=-CUT_EXTRUDE_7_DEPTH, mode=Mode.SUBTRACT)

    # 草图20 → 切除-旋转1 (revolve, cut)
    with BuildSketch(Plane(origin=(0, 62.303737558, 0), x_dir=(0, -1, 0), z_dir=(0.8314696123025378, 0, 0.5555702330196134)), mode=Mode.PRIVATE) as cut_revolve_1_sk:
        Polygon((22.120143808, 175), (-27.879856192, 175), (-27.879856192, 181), (22.120143808, 180), align=None)
    cut_revolve_1 = revolve(cut_revolve_1_sk.sketch.rotate(Axis((97.224790778, 40.18359375, -145.507182153), (0, 1, 0)), 213.75), axis=Axis((97.224790778, 40.18359375, -145.507182153), (0, 1, 0)), mode=Mode.SUBTRACT)

    # 镜向1: 切除-旋转1 across plane
    add(cut_revolve_1.mirror(Plane(origin=(0, 0, 0), x_dir=(0.831469612302494, 0, 0.555570233019679), z_dir=(-0.5555702330196793, 0, 0.8314696123024938))), mode=Mode.SUBTRACT)


solid = part.part
